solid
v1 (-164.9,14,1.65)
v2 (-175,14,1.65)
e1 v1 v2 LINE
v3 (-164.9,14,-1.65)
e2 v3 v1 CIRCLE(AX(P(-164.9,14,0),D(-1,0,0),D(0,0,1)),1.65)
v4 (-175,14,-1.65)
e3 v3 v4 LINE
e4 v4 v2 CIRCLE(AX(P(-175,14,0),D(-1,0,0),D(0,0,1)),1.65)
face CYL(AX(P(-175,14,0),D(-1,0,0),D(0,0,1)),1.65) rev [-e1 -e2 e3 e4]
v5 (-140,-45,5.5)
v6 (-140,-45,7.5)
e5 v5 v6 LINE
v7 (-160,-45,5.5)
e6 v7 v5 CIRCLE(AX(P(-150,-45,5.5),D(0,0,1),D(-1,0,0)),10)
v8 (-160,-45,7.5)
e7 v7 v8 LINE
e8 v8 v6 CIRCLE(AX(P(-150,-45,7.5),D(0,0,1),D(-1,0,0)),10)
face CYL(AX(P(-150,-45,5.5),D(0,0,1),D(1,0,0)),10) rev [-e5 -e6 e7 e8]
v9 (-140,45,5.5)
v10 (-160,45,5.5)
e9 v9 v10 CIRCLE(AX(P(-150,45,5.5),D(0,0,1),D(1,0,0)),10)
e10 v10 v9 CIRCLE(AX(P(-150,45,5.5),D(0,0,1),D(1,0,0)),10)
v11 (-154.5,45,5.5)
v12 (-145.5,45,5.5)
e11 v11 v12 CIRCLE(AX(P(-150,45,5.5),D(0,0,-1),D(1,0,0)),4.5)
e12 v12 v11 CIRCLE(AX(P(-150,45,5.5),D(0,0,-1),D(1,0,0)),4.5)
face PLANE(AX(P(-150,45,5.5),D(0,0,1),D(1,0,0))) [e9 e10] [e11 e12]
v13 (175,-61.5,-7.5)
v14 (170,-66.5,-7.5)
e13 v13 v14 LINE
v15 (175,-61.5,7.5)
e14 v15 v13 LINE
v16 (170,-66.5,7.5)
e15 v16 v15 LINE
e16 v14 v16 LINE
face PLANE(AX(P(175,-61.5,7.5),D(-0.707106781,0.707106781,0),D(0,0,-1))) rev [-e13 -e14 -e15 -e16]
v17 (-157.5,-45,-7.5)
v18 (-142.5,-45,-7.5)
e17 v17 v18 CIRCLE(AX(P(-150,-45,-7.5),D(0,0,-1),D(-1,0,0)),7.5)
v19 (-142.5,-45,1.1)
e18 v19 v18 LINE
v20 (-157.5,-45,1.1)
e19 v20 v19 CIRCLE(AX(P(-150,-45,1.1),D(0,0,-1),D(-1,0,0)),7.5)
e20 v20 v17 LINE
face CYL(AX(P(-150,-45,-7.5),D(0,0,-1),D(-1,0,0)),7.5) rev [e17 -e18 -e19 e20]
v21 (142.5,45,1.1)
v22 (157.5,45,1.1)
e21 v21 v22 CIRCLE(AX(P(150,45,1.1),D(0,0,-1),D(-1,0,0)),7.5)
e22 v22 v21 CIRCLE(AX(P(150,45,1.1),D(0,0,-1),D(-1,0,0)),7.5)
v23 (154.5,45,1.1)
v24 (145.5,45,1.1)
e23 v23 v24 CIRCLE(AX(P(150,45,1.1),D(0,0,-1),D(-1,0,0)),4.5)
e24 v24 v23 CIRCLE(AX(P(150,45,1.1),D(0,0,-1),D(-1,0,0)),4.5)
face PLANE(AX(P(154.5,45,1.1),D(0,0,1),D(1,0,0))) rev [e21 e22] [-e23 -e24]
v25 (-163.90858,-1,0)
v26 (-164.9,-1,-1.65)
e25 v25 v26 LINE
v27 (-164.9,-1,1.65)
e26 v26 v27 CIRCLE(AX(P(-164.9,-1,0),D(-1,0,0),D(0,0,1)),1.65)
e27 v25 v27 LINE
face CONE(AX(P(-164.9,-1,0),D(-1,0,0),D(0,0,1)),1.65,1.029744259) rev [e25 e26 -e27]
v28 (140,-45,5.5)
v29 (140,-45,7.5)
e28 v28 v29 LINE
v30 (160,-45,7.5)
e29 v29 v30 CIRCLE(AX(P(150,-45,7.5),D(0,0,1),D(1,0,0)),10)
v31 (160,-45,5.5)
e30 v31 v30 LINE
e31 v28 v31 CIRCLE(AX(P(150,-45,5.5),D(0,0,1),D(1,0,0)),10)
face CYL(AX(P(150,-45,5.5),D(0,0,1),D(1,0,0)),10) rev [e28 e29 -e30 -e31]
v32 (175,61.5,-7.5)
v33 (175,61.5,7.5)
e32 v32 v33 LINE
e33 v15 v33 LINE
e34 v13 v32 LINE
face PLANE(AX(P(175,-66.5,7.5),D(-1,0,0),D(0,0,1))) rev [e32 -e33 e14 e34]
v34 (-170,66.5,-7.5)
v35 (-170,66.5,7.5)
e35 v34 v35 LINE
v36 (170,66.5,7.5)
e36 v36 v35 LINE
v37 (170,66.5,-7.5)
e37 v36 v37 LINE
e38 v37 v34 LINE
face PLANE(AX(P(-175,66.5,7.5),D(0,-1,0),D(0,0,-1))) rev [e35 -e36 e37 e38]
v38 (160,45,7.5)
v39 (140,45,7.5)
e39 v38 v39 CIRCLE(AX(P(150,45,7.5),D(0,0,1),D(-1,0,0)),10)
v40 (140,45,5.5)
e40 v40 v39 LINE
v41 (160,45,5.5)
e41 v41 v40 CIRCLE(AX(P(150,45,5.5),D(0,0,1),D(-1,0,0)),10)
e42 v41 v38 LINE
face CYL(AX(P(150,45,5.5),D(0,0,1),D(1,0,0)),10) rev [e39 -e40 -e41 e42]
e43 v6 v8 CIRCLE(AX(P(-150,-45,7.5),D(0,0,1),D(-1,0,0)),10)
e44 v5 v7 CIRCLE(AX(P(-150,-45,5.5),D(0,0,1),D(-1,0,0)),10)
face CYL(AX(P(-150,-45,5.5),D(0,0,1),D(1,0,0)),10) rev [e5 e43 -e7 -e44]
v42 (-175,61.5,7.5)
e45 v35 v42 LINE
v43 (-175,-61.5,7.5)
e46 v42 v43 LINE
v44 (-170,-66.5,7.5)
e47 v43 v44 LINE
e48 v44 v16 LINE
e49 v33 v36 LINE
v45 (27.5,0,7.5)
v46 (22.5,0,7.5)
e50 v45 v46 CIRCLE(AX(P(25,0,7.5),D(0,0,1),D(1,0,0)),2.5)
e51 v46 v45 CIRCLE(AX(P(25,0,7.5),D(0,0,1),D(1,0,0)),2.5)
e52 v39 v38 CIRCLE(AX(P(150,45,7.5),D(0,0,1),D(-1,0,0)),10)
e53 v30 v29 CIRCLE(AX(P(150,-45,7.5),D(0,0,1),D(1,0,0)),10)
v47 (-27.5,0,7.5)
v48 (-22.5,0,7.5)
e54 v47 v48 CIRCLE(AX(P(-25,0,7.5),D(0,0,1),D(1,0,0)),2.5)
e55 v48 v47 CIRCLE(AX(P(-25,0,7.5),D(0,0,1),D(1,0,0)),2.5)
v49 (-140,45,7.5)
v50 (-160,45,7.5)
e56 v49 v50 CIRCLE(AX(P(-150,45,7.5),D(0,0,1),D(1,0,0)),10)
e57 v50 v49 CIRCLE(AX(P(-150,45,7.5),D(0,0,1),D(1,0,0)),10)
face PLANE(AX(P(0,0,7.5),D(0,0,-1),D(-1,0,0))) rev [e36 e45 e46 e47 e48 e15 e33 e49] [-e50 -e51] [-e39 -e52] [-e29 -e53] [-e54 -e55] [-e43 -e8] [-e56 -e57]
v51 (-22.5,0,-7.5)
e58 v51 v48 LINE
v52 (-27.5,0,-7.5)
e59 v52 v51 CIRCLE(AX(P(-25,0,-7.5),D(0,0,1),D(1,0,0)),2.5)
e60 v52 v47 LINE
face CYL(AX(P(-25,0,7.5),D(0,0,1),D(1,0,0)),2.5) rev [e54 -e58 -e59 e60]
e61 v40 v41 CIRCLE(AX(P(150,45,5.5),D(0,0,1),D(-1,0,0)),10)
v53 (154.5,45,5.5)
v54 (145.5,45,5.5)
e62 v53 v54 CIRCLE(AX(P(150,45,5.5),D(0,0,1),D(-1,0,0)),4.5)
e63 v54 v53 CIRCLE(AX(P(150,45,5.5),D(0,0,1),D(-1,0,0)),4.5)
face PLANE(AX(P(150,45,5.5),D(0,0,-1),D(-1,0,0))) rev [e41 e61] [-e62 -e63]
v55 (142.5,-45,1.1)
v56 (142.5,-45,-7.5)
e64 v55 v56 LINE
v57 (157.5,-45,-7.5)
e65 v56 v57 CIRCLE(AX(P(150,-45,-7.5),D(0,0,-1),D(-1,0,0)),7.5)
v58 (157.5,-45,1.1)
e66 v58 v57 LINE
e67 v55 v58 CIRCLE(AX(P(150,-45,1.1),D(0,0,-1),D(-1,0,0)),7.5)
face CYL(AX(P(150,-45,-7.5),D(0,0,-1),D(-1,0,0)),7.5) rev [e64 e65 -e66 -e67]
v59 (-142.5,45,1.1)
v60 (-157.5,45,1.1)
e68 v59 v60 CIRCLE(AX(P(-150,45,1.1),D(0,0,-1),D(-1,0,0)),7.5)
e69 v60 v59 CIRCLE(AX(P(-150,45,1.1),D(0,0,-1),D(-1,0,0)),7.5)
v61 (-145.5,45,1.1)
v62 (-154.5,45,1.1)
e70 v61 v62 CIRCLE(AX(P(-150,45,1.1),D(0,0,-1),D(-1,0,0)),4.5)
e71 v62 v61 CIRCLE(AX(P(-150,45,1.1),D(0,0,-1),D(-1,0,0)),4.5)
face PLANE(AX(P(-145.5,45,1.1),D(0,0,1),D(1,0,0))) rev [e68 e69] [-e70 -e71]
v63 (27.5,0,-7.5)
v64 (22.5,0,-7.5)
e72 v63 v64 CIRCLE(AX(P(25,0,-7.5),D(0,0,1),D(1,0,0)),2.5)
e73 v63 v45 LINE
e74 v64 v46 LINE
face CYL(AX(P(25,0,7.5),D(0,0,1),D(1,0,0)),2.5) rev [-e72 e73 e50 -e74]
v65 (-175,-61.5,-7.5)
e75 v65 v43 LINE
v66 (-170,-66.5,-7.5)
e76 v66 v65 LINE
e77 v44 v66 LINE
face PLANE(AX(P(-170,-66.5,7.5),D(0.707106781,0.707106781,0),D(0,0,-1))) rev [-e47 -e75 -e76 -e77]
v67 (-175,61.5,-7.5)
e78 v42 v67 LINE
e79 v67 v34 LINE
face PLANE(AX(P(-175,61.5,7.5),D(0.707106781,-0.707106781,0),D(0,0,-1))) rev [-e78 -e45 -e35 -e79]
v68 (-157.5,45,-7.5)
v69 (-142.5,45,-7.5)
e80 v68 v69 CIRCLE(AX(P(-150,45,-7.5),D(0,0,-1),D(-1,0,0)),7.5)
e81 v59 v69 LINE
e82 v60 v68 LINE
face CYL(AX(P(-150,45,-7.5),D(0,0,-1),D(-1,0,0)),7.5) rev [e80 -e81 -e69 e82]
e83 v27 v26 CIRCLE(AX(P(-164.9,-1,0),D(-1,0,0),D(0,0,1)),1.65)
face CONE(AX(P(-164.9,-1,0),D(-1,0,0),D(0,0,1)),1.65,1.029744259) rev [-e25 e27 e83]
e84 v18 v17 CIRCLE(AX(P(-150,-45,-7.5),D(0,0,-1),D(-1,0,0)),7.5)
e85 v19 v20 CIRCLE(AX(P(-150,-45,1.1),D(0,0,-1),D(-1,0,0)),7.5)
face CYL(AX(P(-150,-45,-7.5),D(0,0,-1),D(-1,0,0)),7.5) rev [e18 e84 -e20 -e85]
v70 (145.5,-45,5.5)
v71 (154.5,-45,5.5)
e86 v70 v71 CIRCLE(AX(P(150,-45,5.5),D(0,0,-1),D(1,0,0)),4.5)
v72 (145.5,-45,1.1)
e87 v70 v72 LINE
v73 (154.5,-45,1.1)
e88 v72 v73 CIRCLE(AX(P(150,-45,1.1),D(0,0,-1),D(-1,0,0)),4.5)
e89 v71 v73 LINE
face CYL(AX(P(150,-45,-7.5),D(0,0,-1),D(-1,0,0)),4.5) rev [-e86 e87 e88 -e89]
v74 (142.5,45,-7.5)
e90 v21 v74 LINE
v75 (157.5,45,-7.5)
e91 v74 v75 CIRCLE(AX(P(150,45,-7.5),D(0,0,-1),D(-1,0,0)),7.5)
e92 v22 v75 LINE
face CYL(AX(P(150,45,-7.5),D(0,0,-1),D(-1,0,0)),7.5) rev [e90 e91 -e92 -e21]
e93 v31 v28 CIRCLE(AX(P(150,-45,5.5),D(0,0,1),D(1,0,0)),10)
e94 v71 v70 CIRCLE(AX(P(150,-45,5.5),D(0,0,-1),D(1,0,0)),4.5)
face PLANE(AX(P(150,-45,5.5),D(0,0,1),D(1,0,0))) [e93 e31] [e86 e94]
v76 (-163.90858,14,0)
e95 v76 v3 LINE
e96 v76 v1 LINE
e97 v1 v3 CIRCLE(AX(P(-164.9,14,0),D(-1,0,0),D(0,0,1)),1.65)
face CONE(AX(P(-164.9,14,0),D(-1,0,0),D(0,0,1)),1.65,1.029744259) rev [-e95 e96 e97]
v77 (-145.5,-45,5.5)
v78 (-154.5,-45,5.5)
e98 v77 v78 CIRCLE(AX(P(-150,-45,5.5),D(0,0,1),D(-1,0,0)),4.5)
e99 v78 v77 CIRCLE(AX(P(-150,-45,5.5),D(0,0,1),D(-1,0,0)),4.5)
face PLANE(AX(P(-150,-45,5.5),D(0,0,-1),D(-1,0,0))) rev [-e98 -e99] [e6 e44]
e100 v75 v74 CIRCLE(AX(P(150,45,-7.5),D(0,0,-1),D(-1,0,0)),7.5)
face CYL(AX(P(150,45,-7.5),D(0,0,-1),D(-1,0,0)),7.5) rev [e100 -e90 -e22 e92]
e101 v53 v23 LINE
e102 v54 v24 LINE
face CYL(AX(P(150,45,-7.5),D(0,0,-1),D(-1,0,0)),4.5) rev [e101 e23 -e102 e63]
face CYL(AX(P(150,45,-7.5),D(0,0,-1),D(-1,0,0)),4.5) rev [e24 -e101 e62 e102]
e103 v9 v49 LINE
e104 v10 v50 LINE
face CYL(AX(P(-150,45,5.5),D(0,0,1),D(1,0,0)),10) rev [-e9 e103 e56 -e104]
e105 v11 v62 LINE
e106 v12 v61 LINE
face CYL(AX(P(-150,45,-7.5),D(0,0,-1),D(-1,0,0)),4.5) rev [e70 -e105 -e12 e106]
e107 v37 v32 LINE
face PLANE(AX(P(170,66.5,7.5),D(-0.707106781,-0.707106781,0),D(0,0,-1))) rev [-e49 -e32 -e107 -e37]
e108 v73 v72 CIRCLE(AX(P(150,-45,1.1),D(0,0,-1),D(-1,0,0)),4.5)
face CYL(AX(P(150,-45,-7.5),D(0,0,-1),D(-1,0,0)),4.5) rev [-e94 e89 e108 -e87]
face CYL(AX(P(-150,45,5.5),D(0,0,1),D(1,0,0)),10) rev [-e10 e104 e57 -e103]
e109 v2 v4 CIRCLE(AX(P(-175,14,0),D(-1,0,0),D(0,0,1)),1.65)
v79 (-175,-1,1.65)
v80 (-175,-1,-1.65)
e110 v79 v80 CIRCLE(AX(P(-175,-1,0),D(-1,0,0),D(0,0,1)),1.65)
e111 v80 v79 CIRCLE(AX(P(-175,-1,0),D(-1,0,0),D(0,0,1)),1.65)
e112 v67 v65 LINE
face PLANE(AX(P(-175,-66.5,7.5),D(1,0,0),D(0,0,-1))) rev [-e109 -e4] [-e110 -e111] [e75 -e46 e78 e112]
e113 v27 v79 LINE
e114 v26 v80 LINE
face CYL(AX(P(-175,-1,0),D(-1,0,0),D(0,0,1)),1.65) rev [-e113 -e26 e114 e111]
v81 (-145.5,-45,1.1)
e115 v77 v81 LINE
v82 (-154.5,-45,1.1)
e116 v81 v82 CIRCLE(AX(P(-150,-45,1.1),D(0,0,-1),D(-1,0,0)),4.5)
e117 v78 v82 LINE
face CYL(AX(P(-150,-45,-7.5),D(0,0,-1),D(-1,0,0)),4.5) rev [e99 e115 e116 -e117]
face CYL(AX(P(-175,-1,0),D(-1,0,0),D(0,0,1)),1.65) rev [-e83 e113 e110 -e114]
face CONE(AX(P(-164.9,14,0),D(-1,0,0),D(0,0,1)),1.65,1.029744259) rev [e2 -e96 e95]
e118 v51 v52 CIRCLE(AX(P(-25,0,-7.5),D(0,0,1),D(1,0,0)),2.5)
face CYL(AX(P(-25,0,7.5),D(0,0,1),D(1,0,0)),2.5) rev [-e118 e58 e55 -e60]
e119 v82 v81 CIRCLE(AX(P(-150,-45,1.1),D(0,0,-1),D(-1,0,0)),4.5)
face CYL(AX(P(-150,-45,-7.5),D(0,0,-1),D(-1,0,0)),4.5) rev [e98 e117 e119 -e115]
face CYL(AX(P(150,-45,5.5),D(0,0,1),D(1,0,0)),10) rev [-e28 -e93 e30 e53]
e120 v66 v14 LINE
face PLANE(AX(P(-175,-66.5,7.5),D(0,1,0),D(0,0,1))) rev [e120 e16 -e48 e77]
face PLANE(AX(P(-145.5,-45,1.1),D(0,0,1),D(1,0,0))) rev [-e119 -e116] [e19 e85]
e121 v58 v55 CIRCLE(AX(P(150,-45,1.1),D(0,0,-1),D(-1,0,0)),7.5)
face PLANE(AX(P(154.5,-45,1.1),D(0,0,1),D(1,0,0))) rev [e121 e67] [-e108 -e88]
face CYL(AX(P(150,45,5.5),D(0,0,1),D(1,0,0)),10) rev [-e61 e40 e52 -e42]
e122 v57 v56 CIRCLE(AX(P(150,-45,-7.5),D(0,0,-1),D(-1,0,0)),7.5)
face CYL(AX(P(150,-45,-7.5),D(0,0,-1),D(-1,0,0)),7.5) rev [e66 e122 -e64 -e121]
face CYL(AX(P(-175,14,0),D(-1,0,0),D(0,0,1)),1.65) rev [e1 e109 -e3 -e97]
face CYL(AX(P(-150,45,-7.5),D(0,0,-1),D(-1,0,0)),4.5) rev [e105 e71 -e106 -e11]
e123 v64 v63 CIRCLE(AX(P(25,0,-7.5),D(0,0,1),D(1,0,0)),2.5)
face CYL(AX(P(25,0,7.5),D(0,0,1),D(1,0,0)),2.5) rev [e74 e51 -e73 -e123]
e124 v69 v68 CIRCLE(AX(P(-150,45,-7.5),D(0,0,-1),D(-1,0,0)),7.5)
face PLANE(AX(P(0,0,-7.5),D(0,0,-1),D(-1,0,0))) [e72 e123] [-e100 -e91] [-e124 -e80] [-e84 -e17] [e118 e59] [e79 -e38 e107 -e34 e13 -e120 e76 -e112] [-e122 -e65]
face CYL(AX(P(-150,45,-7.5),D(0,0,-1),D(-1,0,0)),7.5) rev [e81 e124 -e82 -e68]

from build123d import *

# Parameters (mm, degrees)
SKETCH1_W                                           = 350
SKETCH1_H                                           = 133
BOSS_EXTRUDE1_DEPTH                                 = 7.5
CBORE_FOR_M8_HEX_SOCKET_HEAD_CAP_SCREW1_D           = 9
CBORE_FOR_M8_HEX_SOCKET_HEAD_CAP_SCREW1_CBORE_D     = 15
CBORE_FOR_M8_HEX_SOCKET_HEAD_CAP_SCREW1_CBORE_DEPTH = 8.6
M6_TAPPED_HOLE1_D                                   = 5
SKETCH6_R                                           = 10
CUT_EXTRUDE1_DEPTH                                  = 2
M4_TAPPED_HOLE1_D                                   = 3.3
M4_TAPPED_HOLE1_DEPTH                               = 10.1
M4_TAPPED_HOLE1_TIP                                 = 0.991420021
CHAMFER1_SIZE                                       = 5


with BuildPart() as part:
    # Sketch1 → Boss-Extrude1 (new, symmetric)
    with BuildSketch(Plane.XY):
        Rectangle(SKETCH1_W, SKETCH1_H)
    extrude(amount=BOSS_EXTRUDE1_DEPTH, both=True)

    # CBORE for M8 Hex Socket Head Cap Screw1 (through all)
    with Locations(Plane(origin=(0, 0, -7.5), x_dir=(-1, 0, 0), z_dir=(0, 0, -1))):
        with Locations((-150, 45), (-150, -45), (150, -45), (150, 45)):
            CounterBoreHole(CBORE_FOR_M8_HEX_SOCKET_HEAD_CAP_SCREW1_D / 2, CBORE_FOR_M8_HEX_SOCKET_HEAD_CAP_SCREW1_CBORE_D / 2, CBORE_FOR_M8_HEX_SOCKET_HEAD_CAP_SCREW1_CBORE_DEPTH)

    # M6 Tapped Hole1 (through all)
    with Locations(Plane.XY.offset(7.5)):
        with Locations((-25, 0), (25, 0)):
            Hole(M6_TAPPED_HOLE1_D / 2)

    # Sketch6 → Cut-Extrude1 (cut)
    with BuildSketch(Plane.XY.offset(7.5)):
        with Locations((-150, 45)):
            Circle(SKETCH6_R)
        with Locations(Location((-150, -45, 0), (0, 0, 180))):
            Circle(SKETCH6_R)
        with Locations((150, -45)):
            Circle(SKETCH6_R)
        with Locations(Location((150, 45, 0), (0, 0, 180))):
            Circle(SKETCH6_R)
    extrude(amount=-CUT_EXTRUDE1_DEPTH, mode=Mode.SUBTRACT)

    # M4 Tapped Hole1
    with Locations(Plane.ZY.offset(175)):
        with Locations((0, 14), (0, -1)):
            Hole(M4_TAPPED_HOLE1_D / 2, depth=M4_TAPPED_HOLE1_DEPTH)
            with Locations((0, 0, -(M4_TAPPED_HOLE1_DEPTH + M4_TAPPED_HOLE1_TIP / 2))):  # 118° drill point
                Cone(0, M4_TAPPED_HOLE1_D / 2, M4_TAPPED_HOLE1_TIP, mode=Mode.SUBTRACT)

    # Chamfer1
    chamfer1_edges = [part.edges().sort_by_distance(p)[0] for p in [
        (175, -66.5, 0),
        (-175, -66.5, 0),
        (-175, 66.5, 0),
        (175, 66.5, 0),
    ]]
    chamfer(chamfer1_edges, length=CHAMFER1_SIZE)


solid = part.part
